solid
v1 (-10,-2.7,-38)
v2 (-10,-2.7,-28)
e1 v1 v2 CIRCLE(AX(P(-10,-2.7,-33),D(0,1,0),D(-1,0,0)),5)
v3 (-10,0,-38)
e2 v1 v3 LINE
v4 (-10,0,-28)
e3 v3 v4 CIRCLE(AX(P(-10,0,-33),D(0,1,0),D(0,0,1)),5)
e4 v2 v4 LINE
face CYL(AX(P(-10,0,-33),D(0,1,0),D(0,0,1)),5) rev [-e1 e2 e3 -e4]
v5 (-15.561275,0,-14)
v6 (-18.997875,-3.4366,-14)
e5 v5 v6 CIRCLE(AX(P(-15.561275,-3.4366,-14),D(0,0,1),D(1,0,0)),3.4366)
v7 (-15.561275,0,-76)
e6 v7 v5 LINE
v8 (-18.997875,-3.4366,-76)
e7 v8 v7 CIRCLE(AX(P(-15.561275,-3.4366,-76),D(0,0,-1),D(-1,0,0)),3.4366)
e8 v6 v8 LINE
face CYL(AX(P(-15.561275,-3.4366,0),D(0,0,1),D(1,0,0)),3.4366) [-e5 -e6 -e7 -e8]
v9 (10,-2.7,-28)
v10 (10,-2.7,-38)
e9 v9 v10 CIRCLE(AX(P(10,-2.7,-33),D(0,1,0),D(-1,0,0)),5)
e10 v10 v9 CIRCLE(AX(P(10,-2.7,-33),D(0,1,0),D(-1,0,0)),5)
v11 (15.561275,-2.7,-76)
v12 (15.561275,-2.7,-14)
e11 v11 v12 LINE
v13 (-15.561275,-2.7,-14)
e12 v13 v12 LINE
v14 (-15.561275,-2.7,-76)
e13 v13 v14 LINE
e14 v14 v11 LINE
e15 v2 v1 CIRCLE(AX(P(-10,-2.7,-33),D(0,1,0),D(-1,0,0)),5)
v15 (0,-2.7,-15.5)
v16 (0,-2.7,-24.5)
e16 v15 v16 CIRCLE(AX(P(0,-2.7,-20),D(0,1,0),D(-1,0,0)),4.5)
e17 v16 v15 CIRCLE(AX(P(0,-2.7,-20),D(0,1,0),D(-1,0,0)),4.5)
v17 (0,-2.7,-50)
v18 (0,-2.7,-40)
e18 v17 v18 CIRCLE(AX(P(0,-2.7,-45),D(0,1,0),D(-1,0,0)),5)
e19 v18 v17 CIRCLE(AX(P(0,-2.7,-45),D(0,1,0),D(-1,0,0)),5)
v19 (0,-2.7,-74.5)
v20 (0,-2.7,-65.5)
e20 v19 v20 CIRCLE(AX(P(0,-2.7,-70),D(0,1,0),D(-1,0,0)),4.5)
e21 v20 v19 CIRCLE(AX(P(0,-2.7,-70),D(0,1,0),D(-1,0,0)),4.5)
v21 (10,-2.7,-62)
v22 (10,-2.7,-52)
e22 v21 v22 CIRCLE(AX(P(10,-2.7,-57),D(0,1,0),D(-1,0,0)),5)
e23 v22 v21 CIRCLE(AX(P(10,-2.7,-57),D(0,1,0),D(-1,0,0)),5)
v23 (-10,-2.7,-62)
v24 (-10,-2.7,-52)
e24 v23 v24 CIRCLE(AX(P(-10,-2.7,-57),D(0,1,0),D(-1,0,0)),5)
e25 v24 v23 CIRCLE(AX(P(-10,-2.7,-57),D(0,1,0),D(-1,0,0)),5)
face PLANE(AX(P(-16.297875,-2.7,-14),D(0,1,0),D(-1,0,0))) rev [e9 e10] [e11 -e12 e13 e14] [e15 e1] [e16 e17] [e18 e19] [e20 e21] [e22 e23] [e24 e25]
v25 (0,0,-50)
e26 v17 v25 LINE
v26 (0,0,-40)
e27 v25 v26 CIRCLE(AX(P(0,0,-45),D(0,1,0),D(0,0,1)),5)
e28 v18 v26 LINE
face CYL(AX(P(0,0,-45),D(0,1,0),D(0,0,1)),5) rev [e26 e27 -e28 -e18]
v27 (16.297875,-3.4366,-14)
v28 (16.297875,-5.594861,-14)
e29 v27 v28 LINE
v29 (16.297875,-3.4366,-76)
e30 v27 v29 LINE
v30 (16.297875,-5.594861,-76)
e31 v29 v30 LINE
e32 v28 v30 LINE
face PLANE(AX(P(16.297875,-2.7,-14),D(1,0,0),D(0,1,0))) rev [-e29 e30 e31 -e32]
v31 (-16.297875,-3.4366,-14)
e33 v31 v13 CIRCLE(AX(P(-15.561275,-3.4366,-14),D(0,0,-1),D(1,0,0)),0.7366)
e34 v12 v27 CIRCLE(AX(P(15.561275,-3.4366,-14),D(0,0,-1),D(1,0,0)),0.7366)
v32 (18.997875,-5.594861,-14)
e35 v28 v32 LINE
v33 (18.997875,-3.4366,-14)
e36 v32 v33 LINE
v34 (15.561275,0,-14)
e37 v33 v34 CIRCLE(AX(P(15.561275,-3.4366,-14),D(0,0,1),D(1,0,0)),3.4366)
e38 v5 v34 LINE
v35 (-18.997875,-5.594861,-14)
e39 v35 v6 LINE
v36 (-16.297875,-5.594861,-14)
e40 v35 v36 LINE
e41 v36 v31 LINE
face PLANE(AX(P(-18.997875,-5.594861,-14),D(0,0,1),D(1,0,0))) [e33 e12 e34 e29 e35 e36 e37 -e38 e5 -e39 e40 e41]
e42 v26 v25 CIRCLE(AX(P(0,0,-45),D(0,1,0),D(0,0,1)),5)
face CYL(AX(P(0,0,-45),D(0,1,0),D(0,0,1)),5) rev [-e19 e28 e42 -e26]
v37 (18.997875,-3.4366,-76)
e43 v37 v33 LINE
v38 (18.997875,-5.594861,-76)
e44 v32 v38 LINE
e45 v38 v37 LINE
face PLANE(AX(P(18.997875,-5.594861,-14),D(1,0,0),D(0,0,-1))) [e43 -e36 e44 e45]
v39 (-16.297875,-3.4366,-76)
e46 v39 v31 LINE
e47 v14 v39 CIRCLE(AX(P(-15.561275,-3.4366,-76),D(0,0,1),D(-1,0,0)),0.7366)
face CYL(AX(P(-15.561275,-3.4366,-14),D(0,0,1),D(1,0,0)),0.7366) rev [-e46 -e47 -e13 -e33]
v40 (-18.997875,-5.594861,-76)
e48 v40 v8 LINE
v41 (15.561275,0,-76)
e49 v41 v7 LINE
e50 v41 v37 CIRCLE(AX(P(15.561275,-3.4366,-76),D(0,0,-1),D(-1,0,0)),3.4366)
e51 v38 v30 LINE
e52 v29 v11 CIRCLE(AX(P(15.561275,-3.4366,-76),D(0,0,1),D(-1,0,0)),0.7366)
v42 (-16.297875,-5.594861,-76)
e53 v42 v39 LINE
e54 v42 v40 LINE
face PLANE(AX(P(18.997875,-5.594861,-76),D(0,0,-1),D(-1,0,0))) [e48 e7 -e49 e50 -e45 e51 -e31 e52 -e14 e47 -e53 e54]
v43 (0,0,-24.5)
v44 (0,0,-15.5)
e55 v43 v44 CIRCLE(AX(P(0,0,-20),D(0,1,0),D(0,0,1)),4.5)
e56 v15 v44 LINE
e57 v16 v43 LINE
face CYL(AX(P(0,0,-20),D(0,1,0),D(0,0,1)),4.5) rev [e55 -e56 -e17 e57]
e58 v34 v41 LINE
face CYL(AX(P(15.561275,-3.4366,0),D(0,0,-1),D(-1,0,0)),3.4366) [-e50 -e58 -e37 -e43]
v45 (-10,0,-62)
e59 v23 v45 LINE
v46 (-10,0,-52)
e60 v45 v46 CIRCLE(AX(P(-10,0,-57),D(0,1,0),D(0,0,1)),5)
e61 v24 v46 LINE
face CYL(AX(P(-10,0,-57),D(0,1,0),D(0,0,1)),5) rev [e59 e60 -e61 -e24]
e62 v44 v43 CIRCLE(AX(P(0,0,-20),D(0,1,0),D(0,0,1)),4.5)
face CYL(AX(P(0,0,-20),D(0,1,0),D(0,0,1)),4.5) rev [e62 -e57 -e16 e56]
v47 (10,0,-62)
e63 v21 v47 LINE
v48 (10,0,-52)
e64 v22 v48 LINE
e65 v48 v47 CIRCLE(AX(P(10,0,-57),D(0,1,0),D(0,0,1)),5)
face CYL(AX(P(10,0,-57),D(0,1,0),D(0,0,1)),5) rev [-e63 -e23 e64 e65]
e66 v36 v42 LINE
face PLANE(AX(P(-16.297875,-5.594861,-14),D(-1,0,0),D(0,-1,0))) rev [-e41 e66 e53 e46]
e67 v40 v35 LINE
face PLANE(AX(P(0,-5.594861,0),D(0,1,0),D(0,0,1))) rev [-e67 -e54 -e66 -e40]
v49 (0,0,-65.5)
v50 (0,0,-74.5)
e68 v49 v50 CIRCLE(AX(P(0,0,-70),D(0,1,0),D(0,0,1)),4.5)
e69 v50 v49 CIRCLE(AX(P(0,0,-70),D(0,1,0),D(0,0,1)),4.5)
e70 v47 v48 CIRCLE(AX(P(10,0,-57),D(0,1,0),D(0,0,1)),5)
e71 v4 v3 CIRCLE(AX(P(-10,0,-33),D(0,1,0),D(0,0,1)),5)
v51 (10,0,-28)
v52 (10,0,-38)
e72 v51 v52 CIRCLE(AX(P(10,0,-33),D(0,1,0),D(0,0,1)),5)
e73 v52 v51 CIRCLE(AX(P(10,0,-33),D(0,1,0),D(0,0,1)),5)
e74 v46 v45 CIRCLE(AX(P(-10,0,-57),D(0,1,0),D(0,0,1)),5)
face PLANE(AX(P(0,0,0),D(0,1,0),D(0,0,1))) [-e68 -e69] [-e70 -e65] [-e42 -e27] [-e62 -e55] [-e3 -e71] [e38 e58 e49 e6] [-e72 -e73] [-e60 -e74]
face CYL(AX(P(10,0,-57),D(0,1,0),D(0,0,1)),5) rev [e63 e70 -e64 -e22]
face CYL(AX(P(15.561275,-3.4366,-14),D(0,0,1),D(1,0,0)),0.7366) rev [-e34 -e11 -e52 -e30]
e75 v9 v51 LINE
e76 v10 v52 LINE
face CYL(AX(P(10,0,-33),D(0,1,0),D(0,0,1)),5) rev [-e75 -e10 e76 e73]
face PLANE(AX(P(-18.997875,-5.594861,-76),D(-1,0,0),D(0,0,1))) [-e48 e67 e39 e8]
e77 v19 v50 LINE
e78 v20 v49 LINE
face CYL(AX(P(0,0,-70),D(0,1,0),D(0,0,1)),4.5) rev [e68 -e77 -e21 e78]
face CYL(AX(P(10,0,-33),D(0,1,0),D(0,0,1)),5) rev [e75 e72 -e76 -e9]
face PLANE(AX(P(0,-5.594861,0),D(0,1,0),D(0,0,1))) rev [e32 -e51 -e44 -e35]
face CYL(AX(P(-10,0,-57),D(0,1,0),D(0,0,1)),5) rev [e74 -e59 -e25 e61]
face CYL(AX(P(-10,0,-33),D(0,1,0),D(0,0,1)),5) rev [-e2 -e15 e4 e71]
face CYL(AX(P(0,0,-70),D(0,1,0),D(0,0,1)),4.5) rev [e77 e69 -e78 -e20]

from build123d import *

# Parameters (mm, degrees)
SKETCH1_W                      = 37.995749454
SKETCH1_H                      = 62
BOSS_EXTRUDE1_DEPTH            = 5.594860996
SKETCH2_W                      = 32.595749454
SKETCH2_H                      = 2.894860996
CUT_EXTRUDE1_DEPTH             = 66.086263633
F_10_0_10_DIAMETER_HOLE1_D     = 10
F_10_0_10_DIAMETER_HOLE1_DEPTH = 5.594860996
F_9_0_9_DIAMETER_HOLE1_D       = 9
F_9_0_9_DIAMETER_HOLE1_DEPTH   = 5.594860996
FILLET1_R                      = 0.7366
FILLET2_R                      = 3.4366


with BuildPart() as part:
    # Sketch1 → Boss-Extrude1 (new body)
    with BuildSketch(Plane(origin=(0, 0, 0), x_dir=(1, 0, 0), z_dir=(0, 1, 0))):
        with Locations((0, 45)):
            Rectangle(SKETCH1_W, SKETCH1_H)
    extrude(amount=-BOSS_EXTRUDE1_DEPTH)

    # Sketch2 → Cut-Extrude1 (cut, through all)
    with BuildSketch(Plane(origin=(0, 0, -76), x_dir=(-1, 0, 0), z_dir=(0, 0, -1))):
        with Locations((0, -4.147430498)):
            Rectangle(SKETCH2_W, SKETCH2_H)
    extrude(amount=-CUT_EXTRUDE1_DEPTH, mode=Mode.SUBTRACT)

    # Ø10.0 (10) Diameter Hole1
    with Locations(Plane(origin=(0, 0, 0), x_dir=(1, 0, 0), z_dir=(0, 1, 0))):
        with Locations((0, 45), (-10, 57), (-10, 33), (10, 33), (10, 57)):
            Hole(F_10_0_10_DIAMETER_HOLE1_D / 2, depth=F_10_0_10_DIAMETER_HOLE1_DEPTH)

    # Ø9.0 (9) Diameter Hole1
    with Locations(Plane(origin=(0, 0, 0), x_dir=(1, 0, 0), z_dir=(0, 1, 0))):
        with Locations((0, 70), (0, 20)):
            Hole(F_9_0_9_DIAMETER_HOLE1_D / 2, depth=F_9_0_9_DIAMETER_HOLE1_DEPTH)

    # Fillet1
    fillet1_edges = [part.edges().sort_by_distance(p)[0] for p in [
        (16.297874727, -2.7, -45),
        (-16.297874727, -2.7, -45),
    ]]
    fillet(fillet1_edges, radius=FILLET1_R)

    # Fillet2
    fillet2_edges = [part.edges().sort_by_distance(p)[0] for p in [
        (18.997874727, 0, -45),
        (-18.997874727, 0, -45),
    ]]
    fillet(fillet2_edges, radius=FILLET2_R)


solid = part.part
